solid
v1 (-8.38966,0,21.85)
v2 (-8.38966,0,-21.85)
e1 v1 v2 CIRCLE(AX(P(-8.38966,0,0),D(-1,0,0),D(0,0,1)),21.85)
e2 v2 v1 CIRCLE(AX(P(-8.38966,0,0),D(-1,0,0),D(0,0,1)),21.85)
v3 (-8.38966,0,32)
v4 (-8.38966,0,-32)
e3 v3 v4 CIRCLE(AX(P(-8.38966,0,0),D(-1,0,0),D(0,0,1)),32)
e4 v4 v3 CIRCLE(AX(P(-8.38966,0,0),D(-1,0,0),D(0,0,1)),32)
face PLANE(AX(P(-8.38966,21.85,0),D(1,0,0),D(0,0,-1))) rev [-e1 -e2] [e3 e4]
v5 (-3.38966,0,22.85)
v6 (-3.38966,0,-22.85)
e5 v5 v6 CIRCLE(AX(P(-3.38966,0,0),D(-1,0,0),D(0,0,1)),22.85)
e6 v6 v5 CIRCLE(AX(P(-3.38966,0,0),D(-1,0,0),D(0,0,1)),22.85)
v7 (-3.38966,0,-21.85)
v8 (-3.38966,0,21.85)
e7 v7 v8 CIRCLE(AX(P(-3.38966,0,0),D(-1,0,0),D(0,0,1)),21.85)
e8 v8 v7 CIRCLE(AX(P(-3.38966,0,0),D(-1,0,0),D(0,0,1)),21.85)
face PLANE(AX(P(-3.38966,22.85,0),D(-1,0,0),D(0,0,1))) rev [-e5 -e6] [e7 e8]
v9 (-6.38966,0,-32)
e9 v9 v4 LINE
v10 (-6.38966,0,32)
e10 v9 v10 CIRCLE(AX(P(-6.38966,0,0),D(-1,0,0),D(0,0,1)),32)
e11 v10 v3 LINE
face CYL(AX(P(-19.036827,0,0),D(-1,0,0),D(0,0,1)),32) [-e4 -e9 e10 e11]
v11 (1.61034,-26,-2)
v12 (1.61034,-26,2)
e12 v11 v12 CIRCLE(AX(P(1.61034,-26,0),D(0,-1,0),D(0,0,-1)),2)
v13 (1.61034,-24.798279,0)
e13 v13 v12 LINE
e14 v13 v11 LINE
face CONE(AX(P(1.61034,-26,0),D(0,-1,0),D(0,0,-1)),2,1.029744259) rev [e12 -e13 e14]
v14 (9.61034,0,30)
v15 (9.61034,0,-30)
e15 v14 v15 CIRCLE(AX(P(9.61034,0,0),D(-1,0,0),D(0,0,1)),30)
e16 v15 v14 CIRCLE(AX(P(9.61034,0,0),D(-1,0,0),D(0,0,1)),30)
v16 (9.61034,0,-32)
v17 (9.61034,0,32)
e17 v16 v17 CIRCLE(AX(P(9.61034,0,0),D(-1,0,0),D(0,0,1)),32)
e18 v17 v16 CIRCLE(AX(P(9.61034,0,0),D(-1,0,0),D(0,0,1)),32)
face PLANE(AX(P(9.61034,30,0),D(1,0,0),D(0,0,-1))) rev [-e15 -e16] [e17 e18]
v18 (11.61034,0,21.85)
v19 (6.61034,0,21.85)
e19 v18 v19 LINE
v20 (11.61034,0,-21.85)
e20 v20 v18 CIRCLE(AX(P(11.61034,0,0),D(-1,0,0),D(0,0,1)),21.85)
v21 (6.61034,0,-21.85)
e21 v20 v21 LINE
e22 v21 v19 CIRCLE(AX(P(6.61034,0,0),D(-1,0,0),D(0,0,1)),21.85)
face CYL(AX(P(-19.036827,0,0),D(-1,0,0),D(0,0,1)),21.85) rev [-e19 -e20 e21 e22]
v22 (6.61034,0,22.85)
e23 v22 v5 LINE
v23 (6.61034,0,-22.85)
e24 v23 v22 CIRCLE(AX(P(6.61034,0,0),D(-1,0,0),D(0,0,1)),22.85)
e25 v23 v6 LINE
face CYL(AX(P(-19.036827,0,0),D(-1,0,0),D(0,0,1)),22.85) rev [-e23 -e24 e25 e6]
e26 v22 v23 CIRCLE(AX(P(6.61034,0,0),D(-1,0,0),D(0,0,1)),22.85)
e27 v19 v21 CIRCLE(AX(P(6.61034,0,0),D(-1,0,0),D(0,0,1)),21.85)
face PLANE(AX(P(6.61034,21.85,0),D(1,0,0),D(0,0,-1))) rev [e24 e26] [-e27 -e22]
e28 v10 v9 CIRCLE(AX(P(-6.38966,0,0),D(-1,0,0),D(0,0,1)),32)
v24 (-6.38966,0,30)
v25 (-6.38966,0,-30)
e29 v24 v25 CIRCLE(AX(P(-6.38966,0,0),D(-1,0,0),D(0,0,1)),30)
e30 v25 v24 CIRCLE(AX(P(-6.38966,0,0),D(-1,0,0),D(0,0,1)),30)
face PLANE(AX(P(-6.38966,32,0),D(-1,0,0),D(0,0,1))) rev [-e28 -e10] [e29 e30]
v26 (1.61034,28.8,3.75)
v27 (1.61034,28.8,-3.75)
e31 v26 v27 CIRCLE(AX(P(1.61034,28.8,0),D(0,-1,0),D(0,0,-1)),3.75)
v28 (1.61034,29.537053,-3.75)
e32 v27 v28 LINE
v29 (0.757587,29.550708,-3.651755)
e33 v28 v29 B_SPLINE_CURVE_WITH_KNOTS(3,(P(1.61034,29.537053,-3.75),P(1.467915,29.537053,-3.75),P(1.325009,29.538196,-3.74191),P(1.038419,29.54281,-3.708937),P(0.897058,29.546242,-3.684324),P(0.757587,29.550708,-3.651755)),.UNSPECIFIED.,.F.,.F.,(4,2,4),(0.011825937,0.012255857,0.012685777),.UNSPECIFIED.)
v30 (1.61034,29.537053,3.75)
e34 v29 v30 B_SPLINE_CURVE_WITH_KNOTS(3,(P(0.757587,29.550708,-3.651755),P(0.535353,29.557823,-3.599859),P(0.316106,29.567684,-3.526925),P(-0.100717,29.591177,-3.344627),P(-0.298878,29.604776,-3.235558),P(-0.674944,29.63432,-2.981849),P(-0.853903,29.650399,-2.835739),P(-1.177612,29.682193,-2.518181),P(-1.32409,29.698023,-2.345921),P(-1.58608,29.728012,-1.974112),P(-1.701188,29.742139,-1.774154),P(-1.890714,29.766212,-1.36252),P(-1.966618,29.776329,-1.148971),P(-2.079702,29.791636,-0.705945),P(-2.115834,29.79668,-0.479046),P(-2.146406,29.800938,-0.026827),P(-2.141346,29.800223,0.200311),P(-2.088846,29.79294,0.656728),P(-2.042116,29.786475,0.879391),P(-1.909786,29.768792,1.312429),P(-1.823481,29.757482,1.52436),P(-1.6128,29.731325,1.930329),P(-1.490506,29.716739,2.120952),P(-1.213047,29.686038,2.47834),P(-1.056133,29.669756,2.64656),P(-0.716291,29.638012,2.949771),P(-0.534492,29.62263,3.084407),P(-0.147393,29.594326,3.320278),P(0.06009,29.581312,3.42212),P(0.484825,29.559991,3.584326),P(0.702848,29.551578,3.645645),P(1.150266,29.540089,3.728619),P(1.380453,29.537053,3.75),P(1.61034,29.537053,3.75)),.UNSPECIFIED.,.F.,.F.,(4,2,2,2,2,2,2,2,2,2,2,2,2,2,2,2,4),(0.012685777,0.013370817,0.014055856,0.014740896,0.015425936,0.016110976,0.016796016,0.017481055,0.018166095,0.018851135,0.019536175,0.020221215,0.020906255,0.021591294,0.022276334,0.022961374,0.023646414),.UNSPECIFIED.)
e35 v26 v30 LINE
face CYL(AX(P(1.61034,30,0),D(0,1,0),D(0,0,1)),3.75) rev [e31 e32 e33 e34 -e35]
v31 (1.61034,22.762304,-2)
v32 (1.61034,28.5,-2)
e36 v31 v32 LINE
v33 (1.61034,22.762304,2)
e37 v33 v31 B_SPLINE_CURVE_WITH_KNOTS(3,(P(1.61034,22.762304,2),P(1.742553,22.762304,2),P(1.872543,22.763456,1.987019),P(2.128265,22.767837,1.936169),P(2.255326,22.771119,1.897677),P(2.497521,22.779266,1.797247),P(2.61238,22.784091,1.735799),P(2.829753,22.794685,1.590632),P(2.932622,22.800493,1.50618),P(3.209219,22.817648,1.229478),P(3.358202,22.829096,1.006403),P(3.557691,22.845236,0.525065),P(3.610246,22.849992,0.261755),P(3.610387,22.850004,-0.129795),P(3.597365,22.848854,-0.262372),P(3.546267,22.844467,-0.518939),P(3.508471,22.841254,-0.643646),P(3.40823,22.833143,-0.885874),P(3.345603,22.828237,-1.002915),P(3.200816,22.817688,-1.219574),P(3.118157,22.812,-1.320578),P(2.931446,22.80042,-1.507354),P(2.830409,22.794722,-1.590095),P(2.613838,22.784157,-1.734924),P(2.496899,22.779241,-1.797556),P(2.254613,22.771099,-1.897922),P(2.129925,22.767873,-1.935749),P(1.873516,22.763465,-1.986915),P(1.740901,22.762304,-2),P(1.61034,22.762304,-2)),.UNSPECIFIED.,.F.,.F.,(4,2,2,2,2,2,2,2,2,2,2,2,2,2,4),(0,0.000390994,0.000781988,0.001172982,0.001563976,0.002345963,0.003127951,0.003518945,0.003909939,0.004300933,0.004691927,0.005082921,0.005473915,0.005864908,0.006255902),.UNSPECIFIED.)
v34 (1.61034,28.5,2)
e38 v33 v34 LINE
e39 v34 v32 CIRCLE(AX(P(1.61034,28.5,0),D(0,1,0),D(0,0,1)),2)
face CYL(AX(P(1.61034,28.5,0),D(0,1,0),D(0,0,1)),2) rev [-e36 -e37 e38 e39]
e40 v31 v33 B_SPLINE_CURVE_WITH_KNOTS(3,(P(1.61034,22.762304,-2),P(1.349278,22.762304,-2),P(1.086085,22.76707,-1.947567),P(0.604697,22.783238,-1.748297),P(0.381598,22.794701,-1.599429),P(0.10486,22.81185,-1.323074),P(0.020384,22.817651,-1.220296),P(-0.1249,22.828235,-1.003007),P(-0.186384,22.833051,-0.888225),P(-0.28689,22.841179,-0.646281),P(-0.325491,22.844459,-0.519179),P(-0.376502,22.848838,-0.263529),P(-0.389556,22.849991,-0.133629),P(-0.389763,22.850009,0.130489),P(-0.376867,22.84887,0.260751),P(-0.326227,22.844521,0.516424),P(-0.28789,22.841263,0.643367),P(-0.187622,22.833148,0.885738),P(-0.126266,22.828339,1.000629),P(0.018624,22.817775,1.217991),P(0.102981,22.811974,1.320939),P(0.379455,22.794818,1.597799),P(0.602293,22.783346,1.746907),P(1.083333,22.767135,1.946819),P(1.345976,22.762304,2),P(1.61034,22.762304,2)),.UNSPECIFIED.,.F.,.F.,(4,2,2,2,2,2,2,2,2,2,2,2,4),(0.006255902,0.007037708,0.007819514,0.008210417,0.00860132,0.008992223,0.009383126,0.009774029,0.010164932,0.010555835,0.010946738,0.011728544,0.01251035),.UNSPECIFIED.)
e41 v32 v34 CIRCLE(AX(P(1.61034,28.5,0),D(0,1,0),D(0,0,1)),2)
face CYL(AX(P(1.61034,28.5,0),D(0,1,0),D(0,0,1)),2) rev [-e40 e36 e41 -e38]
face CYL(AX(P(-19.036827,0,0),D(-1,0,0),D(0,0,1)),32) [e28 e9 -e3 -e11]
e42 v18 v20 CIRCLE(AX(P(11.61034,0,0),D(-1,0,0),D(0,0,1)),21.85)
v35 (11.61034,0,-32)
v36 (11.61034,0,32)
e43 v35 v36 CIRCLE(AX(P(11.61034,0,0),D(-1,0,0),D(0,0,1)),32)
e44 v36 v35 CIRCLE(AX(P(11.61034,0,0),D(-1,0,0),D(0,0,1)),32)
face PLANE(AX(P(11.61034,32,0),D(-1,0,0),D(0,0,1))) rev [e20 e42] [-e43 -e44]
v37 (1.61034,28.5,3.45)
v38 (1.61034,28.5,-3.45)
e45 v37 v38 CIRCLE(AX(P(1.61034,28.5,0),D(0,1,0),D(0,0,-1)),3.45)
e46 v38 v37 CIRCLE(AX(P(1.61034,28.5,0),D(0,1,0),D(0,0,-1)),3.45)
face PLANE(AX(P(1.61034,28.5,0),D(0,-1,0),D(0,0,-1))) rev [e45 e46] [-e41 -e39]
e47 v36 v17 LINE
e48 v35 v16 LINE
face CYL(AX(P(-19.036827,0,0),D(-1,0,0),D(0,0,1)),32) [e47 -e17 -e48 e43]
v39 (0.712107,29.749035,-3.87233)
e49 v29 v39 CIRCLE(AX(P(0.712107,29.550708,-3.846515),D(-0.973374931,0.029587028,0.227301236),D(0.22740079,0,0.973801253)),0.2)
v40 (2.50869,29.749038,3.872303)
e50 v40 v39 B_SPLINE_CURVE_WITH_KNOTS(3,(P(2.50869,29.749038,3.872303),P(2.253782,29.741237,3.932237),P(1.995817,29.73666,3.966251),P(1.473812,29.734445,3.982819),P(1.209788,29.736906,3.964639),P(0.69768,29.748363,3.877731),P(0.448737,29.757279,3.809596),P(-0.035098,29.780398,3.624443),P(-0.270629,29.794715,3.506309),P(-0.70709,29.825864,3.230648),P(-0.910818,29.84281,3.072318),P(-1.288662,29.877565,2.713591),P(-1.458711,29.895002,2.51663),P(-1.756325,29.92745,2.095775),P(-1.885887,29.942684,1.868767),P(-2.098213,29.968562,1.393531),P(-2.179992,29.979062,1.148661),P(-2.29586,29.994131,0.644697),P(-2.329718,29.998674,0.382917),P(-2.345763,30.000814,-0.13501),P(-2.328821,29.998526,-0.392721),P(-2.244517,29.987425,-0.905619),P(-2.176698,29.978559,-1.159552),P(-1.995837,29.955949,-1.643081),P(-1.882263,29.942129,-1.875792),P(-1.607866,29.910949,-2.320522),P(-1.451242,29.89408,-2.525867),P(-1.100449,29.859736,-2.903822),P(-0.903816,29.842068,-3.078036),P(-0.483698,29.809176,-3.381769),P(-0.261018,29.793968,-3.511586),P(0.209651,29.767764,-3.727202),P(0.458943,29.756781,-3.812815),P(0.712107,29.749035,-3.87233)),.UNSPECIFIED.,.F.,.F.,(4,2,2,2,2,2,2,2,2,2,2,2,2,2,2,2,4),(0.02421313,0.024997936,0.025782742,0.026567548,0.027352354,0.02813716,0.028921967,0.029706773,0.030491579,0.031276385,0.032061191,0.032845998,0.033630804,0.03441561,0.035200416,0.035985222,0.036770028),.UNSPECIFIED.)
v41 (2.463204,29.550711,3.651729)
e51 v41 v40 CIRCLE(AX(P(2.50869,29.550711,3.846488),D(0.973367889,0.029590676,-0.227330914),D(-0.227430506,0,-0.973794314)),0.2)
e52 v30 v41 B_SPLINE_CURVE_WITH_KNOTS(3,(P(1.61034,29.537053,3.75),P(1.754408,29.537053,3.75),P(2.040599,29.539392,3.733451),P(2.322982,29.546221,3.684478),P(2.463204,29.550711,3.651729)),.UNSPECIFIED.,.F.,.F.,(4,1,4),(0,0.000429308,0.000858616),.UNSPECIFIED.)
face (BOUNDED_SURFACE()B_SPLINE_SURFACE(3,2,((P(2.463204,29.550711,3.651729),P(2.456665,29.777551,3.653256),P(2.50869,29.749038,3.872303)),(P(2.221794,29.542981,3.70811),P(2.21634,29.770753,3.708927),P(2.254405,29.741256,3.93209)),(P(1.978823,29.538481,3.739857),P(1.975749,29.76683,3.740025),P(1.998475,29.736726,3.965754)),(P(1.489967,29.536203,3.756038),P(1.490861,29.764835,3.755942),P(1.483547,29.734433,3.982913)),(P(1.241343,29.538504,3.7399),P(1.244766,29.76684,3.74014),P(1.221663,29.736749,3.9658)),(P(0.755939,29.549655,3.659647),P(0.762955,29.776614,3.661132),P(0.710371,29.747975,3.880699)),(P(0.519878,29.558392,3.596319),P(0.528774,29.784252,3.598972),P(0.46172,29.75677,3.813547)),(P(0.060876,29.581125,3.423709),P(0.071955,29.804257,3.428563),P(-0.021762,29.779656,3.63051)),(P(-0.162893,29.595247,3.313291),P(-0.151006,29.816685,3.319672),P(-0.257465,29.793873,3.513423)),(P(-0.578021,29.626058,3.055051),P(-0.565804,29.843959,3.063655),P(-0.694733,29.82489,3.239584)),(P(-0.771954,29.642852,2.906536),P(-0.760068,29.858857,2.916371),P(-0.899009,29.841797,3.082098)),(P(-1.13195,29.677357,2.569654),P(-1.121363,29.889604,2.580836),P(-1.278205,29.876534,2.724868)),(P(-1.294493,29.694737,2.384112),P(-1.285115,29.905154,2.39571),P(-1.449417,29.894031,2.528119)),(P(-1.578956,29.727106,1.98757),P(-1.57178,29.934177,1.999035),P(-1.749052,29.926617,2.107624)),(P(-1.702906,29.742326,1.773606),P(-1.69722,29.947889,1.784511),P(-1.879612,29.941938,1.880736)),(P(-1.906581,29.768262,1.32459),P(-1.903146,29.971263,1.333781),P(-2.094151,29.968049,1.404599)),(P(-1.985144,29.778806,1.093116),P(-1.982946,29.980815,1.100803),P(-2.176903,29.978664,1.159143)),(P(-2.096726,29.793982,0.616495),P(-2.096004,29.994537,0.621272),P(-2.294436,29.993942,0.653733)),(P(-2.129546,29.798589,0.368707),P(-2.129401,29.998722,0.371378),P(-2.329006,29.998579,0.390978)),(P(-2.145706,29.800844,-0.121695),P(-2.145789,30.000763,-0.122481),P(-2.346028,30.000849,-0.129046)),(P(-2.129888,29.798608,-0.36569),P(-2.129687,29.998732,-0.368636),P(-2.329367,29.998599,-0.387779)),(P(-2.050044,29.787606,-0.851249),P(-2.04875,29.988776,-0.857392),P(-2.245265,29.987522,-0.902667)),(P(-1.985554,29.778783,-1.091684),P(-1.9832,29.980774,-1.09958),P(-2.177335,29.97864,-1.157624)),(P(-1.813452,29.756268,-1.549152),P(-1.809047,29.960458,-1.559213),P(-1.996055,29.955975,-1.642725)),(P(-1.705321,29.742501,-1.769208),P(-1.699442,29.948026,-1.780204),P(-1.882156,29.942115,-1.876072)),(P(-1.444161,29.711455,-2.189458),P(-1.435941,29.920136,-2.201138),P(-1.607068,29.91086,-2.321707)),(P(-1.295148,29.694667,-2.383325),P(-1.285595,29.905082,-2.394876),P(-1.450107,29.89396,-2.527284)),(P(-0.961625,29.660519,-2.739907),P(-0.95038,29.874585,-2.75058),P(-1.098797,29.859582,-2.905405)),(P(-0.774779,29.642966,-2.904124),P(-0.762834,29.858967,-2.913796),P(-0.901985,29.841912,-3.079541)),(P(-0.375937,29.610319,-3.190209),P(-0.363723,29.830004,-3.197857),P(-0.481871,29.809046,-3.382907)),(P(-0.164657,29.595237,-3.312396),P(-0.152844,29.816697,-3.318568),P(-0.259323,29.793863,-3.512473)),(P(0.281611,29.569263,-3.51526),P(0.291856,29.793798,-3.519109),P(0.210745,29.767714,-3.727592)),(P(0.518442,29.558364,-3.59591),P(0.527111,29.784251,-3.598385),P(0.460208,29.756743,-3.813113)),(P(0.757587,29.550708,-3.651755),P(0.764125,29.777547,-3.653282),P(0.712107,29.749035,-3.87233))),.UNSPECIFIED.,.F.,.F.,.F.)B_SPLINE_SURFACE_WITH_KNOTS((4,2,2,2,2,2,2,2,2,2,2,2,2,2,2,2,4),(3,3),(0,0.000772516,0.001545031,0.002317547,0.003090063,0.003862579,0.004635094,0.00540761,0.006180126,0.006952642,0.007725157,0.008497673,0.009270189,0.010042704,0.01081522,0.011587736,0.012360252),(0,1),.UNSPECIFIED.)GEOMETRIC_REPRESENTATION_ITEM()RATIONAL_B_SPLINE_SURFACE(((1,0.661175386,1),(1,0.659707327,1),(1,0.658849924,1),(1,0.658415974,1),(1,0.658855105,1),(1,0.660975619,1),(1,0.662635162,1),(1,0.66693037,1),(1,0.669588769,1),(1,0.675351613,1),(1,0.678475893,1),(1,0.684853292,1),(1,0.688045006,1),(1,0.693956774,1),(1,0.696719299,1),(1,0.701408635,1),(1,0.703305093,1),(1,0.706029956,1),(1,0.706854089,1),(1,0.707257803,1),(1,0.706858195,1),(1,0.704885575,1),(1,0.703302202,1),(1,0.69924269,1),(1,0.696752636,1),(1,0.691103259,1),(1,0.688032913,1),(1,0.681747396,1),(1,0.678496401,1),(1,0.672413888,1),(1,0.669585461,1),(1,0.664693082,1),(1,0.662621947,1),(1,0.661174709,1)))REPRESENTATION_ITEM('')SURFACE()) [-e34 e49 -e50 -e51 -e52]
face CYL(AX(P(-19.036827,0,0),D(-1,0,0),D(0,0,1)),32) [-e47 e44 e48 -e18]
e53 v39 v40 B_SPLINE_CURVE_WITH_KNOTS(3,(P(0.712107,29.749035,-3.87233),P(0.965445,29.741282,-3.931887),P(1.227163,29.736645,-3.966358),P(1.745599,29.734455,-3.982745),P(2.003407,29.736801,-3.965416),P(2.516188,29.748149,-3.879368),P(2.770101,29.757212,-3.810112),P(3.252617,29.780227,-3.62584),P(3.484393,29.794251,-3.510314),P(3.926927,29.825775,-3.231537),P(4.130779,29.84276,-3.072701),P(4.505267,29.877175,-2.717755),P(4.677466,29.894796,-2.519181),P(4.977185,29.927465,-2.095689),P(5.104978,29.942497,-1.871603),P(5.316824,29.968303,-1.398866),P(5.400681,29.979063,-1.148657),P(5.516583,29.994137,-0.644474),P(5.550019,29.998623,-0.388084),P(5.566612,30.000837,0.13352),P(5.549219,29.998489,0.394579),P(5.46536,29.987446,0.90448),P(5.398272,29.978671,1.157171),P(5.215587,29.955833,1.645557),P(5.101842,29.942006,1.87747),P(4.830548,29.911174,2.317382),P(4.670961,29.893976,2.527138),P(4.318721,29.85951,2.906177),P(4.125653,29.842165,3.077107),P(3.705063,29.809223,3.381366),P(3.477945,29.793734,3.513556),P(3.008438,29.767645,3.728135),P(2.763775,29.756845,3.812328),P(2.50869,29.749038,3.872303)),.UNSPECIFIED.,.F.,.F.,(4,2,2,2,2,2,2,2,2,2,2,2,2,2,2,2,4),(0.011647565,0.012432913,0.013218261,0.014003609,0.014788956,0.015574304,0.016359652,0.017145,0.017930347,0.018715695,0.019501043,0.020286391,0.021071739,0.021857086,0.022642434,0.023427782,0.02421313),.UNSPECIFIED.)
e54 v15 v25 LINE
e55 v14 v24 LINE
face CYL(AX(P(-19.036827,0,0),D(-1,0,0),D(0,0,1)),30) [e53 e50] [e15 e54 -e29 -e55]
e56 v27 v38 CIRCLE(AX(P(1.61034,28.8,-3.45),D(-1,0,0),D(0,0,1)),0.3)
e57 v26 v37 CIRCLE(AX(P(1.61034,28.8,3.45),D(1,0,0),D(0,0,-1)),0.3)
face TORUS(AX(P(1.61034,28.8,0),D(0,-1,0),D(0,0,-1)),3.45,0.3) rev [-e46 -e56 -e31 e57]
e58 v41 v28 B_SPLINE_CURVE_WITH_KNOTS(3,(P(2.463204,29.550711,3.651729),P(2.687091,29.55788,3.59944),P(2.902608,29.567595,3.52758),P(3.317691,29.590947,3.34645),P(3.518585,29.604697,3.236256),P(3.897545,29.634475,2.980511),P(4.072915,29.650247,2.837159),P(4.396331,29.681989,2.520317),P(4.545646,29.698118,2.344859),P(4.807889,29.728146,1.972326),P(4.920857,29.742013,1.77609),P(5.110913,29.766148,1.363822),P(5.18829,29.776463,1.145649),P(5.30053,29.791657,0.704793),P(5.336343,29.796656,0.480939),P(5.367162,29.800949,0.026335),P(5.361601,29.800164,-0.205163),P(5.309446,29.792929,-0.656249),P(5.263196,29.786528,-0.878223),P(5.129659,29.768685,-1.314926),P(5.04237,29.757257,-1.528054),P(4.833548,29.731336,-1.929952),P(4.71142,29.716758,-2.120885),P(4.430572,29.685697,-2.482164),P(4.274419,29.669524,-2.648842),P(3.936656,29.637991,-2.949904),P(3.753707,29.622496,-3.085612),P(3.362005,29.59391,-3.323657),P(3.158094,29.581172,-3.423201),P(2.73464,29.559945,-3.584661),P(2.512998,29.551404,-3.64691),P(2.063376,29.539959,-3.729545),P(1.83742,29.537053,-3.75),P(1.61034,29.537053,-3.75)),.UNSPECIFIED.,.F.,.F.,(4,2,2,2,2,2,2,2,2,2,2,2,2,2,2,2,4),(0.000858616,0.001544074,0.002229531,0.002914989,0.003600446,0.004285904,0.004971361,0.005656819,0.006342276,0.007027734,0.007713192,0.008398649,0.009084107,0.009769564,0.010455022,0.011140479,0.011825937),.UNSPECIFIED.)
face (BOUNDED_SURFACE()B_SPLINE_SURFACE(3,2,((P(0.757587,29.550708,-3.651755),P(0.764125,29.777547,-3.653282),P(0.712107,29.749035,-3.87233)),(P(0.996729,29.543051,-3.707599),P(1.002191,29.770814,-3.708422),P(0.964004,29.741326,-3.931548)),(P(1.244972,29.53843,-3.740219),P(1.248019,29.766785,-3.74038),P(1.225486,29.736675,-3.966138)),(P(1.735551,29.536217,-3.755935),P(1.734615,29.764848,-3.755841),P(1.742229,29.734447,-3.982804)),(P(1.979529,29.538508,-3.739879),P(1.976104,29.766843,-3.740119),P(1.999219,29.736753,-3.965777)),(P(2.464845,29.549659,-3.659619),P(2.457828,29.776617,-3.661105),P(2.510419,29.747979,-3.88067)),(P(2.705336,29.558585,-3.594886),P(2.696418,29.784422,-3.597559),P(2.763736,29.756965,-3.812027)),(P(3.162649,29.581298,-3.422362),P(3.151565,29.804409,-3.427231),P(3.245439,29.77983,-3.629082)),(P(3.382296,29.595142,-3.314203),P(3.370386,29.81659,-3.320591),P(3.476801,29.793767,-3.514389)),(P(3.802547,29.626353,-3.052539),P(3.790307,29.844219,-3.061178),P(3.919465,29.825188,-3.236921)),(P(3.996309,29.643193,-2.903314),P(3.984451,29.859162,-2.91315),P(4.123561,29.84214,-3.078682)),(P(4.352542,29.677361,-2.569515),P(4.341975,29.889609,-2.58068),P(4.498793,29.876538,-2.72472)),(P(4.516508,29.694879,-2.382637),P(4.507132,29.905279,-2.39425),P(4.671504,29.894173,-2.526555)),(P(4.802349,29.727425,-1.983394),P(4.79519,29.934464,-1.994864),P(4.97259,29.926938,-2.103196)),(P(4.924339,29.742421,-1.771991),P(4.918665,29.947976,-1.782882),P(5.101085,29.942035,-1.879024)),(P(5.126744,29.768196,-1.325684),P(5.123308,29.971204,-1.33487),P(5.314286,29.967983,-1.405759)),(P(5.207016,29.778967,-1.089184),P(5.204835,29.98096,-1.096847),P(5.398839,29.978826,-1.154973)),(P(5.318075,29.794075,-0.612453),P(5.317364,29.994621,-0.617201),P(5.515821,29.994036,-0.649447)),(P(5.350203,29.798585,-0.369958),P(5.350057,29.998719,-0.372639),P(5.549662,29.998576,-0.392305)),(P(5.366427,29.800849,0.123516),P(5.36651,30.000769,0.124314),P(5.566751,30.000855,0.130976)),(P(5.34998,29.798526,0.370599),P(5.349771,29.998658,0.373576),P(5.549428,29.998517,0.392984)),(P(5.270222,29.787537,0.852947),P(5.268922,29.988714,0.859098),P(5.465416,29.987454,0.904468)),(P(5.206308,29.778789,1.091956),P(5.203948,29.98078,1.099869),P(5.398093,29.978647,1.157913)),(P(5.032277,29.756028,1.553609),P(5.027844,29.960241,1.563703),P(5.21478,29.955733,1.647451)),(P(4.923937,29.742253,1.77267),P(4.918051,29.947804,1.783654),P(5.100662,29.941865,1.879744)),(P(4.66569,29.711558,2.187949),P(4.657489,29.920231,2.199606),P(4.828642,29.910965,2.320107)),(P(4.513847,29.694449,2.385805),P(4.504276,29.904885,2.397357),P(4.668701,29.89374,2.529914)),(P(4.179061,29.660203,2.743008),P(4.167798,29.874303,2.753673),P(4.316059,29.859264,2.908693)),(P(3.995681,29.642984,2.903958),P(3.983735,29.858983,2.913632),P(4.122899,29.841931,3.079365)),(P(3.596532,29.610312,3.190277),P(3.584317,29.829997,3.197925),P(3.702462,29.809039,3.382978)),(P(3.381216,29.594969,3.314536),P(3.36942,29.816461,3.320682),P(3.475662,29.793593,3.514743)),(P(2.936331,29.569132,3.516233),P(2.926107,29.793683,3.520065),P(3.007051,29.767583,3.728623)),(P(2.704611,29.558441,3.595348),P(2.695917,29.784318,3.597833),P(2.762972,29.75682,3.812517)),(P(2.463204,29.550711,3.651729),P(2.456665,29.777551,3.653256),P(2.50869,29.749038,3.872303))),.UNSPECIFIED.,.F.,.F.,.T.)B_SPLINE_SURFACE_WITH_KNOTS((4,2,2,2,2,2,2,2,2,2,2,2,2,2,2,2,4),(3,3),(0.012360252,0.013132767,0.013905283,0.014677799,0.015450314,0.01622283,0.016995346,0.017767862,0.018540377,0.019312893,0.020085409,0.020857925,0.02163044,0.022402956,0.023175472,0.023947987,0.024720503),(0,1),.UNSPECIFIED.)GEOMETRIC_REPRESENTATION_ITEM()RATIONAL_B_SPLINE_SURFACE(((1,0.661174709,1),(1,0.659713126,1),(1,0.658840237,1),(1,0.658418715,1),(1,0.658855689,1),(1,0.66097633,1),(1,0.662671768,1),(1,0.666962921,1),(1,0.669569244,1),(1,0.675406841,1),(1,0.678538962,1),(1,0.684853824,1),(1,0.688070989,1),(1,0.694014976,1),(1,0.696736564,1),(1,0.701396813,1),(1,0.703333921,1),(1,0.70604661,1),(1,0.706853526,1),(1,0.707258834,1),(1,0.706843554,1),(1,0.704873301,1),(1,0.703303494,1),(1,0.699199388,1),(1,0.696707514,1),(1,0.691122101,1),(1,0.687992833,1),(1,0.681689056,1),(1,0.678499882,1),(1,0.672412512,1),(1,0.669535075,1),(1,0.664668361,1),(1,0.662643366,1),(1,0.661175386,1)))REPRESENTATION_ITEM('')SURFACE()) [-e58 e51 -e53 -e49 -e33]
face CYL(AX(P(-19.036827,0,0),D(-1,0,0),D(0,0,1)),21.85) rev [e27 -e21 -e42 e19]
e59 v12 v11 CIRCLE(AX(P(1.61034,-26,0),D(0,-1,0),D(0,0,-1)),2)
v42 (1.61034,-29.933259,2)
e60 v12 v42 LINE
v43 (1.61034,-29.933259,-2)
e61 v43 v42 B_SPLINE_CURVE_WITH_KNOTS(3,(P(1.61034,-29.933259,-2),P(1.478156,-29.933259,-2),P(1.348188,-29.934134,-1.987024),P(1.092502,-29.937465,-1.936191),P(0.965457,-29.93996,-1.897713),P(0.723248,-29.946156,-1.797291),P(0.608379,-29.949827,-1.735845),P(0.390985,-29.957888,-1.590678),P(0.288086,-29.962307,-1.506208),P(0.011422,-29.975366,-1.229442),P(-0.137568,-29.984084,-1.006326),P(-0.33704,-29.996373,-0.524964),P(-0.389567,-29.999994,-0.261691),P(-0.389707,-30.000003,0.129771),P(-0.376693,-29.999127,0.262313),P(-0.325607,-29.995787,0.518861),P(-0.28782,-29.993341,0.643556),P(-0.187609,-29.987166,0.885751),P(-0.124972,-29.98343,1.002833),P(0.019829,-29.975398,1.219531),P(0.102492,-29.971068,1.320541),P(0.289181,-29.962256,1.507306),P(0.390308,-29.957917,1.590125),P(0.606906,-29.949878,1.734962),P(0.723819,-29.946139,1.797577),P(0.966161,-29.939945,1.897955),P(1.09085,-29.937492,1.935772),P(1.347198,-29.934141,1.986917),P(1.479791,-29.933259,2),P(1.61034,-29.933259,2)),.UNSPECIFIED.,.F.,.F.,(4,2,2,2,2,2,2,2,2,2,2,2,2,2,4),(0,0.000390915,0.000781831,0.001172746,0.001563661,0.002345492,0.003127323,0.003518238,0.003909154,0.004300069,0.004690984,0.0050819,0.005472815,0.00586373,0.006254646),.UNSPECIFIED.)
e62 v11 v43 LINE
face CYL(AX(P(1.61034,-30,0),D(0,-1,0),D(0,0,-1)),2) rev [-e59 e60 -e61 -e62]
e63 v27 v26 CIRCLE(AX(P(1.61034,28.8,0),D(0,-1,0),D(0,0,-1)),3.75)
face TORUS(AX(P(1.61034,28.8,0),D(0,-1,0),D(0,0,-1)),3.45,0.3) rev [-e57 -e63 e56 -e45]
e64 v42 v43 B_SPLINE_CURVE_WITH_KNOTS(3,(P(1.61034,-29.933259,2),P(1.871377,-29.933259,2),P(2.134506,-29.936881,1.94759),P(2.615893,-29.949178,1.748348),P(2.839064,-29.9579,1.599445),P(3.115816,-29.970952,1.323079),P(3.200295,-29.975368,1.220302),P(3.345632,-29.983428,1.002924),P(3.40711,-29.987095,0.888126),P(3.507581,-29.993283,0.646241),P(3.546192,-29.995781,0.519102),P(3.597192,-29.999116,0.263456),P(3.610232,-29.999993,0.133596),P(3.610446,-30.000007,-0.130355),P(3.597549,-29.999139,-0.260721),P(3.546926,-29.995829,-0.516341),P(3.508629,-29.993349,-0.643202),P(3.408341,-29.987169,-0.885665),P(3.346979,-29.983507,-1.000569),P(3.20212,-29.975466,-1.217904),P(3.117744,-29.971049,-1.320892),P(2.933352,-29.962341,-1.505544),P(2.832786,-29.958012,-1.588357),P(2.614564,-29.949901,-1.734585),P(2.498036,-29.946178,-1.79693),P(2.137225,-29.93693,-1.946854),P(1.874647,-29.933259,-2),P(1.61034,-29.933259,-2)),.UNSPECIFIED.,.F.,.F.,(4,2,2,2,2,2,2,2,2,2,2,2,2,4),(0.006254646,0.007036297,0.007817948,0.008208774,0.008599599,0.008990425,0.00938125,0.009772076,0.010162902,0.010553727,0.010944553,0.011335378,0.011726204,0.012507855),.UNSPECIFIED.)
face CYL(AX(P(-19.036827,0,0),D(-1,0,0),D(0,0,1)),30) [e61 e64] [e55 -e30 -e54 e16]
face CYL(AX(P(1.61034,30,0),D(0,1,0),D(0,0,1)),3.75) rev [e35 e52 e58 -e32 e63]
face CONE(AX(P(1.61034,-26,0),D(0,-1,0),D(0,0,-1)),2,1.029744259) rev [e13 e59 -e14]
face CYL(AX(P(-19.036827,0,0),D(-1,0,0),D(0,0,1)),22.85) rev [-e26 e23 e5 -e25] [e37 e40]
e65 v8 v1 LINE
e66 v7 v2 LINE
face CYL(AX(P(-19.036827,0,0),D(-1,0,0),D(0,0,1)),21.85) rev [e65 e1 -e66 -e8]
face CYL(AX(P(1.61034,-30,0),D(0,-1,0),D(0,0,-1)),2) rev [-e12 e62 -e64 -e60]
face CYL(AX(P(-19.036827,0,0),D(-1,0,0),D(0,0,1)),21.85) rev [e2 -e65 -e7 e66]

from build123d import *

# Parameters (mm, degrees)
HOLE1_D           = 7.5
HOLE1_DEPTH       = 1.5
HOLE2_REACH       = 71.419
HOLE2_BORE_R      = 2
DOWEL_HOLE1_D     = 4
DOWEL_HOLE1_DEPTH = 4
DOWEL_HOLE1_TIP   = 1.201721238
FILLET1_R         = 0.2
FILLET2_R         = 0.3


with BuildPart() as part:
    # Sketch1 → Revolve1 (revolve)
    with BuildSketch(Plane.XY, mode=Mode.PRIVATE) as revolve1_sk:
        Polygon((-8.389660143, 21.85), (-8.389660143, 32), (-6.389660143, 32), (-6.389660143, 30), (9.610339857, 30), (9.610339857, 32), (11.610339857, 32), (11.610339857, 21.85), (6.610339857, 21.85), (6.610339857, 22.85), (-3.389660143, 22.85), (-3.389660143, 21.85), align=None)
    revolve(revolve1_sk.sketch.rotate(Axis((-19.036826505, 0, 0), (1, 0, 0)), 90), axis=Axis((-19.036826505, 0, 0), (1, 0, 0)))

    # Hole1
    with Locations(Plane(origin=(0, 30, 0), x_dir=(1, 0, 0), z_dir=(0, 1, 0))):
        with Locations((1.610339857, 0)):
            Hole(HOLE1_D / 2, depth=HOLE1_DEPTH)

    # Hole2 bore → Hole2 (cut, up to next)
    with BuildSketch(Plane(origin=(0, 28.5, 0), x_dir=(1, 0, 0), z_dir=(0, 1, 0)), mode=Mode.PRIVATE) as hole2_sk1:
        with Locations((1.610339857, 0)):
            Circle(HOLE2_BORE_R)
    hole2_tool1 = extrude(hole2_sk1.sketch, amount=-HOLE2_REACH, mode=Mode.PRIVATE) & part.part
    add(hole2_tool1.solids().sort_by_distance((1.61034, 28.5, 0))[0], mode=Mode.SUBTRACT)

    # Dowel Hole1
    with Locations(Plane(origin=(0, -30, 0), x_dir=(-1, 0, 0), z_dir=(0, -1, 0))):
        with Locations((-1.610339857, 0)):
            Hole(DOWEL_HOLE1_D / 2, depth=DOWEL_HOLE1_DEPTH)
            with Locations((0, 0, -(DOWEL_HOLE1_DEPTH + DOWEL_HOLE1_TIP / 2))):  # 118° drill point
                Cone(0, DOWEL_HOLE1_D / 2, DOWEL_HOLE1_TIP, mode=Mode.SUBTRACT)

    # Fillet1
    fillet1_edges = [part.edges().sort_by_distance(p)[0] for p in [
        (5.360339864, 29.999999997, -1e-09),
    ]]
    fillet(fillet1_edges, radius=FILLET1_R)

    # Fillet2
    fillet2_edges = [part.edges().sort_by_distance(p)[0] for p in [
        (5.360339857, 28.5, 0),
    ]]
    fillet(fillet2_edges, radius=FILLET2_R)


solid = part.part
